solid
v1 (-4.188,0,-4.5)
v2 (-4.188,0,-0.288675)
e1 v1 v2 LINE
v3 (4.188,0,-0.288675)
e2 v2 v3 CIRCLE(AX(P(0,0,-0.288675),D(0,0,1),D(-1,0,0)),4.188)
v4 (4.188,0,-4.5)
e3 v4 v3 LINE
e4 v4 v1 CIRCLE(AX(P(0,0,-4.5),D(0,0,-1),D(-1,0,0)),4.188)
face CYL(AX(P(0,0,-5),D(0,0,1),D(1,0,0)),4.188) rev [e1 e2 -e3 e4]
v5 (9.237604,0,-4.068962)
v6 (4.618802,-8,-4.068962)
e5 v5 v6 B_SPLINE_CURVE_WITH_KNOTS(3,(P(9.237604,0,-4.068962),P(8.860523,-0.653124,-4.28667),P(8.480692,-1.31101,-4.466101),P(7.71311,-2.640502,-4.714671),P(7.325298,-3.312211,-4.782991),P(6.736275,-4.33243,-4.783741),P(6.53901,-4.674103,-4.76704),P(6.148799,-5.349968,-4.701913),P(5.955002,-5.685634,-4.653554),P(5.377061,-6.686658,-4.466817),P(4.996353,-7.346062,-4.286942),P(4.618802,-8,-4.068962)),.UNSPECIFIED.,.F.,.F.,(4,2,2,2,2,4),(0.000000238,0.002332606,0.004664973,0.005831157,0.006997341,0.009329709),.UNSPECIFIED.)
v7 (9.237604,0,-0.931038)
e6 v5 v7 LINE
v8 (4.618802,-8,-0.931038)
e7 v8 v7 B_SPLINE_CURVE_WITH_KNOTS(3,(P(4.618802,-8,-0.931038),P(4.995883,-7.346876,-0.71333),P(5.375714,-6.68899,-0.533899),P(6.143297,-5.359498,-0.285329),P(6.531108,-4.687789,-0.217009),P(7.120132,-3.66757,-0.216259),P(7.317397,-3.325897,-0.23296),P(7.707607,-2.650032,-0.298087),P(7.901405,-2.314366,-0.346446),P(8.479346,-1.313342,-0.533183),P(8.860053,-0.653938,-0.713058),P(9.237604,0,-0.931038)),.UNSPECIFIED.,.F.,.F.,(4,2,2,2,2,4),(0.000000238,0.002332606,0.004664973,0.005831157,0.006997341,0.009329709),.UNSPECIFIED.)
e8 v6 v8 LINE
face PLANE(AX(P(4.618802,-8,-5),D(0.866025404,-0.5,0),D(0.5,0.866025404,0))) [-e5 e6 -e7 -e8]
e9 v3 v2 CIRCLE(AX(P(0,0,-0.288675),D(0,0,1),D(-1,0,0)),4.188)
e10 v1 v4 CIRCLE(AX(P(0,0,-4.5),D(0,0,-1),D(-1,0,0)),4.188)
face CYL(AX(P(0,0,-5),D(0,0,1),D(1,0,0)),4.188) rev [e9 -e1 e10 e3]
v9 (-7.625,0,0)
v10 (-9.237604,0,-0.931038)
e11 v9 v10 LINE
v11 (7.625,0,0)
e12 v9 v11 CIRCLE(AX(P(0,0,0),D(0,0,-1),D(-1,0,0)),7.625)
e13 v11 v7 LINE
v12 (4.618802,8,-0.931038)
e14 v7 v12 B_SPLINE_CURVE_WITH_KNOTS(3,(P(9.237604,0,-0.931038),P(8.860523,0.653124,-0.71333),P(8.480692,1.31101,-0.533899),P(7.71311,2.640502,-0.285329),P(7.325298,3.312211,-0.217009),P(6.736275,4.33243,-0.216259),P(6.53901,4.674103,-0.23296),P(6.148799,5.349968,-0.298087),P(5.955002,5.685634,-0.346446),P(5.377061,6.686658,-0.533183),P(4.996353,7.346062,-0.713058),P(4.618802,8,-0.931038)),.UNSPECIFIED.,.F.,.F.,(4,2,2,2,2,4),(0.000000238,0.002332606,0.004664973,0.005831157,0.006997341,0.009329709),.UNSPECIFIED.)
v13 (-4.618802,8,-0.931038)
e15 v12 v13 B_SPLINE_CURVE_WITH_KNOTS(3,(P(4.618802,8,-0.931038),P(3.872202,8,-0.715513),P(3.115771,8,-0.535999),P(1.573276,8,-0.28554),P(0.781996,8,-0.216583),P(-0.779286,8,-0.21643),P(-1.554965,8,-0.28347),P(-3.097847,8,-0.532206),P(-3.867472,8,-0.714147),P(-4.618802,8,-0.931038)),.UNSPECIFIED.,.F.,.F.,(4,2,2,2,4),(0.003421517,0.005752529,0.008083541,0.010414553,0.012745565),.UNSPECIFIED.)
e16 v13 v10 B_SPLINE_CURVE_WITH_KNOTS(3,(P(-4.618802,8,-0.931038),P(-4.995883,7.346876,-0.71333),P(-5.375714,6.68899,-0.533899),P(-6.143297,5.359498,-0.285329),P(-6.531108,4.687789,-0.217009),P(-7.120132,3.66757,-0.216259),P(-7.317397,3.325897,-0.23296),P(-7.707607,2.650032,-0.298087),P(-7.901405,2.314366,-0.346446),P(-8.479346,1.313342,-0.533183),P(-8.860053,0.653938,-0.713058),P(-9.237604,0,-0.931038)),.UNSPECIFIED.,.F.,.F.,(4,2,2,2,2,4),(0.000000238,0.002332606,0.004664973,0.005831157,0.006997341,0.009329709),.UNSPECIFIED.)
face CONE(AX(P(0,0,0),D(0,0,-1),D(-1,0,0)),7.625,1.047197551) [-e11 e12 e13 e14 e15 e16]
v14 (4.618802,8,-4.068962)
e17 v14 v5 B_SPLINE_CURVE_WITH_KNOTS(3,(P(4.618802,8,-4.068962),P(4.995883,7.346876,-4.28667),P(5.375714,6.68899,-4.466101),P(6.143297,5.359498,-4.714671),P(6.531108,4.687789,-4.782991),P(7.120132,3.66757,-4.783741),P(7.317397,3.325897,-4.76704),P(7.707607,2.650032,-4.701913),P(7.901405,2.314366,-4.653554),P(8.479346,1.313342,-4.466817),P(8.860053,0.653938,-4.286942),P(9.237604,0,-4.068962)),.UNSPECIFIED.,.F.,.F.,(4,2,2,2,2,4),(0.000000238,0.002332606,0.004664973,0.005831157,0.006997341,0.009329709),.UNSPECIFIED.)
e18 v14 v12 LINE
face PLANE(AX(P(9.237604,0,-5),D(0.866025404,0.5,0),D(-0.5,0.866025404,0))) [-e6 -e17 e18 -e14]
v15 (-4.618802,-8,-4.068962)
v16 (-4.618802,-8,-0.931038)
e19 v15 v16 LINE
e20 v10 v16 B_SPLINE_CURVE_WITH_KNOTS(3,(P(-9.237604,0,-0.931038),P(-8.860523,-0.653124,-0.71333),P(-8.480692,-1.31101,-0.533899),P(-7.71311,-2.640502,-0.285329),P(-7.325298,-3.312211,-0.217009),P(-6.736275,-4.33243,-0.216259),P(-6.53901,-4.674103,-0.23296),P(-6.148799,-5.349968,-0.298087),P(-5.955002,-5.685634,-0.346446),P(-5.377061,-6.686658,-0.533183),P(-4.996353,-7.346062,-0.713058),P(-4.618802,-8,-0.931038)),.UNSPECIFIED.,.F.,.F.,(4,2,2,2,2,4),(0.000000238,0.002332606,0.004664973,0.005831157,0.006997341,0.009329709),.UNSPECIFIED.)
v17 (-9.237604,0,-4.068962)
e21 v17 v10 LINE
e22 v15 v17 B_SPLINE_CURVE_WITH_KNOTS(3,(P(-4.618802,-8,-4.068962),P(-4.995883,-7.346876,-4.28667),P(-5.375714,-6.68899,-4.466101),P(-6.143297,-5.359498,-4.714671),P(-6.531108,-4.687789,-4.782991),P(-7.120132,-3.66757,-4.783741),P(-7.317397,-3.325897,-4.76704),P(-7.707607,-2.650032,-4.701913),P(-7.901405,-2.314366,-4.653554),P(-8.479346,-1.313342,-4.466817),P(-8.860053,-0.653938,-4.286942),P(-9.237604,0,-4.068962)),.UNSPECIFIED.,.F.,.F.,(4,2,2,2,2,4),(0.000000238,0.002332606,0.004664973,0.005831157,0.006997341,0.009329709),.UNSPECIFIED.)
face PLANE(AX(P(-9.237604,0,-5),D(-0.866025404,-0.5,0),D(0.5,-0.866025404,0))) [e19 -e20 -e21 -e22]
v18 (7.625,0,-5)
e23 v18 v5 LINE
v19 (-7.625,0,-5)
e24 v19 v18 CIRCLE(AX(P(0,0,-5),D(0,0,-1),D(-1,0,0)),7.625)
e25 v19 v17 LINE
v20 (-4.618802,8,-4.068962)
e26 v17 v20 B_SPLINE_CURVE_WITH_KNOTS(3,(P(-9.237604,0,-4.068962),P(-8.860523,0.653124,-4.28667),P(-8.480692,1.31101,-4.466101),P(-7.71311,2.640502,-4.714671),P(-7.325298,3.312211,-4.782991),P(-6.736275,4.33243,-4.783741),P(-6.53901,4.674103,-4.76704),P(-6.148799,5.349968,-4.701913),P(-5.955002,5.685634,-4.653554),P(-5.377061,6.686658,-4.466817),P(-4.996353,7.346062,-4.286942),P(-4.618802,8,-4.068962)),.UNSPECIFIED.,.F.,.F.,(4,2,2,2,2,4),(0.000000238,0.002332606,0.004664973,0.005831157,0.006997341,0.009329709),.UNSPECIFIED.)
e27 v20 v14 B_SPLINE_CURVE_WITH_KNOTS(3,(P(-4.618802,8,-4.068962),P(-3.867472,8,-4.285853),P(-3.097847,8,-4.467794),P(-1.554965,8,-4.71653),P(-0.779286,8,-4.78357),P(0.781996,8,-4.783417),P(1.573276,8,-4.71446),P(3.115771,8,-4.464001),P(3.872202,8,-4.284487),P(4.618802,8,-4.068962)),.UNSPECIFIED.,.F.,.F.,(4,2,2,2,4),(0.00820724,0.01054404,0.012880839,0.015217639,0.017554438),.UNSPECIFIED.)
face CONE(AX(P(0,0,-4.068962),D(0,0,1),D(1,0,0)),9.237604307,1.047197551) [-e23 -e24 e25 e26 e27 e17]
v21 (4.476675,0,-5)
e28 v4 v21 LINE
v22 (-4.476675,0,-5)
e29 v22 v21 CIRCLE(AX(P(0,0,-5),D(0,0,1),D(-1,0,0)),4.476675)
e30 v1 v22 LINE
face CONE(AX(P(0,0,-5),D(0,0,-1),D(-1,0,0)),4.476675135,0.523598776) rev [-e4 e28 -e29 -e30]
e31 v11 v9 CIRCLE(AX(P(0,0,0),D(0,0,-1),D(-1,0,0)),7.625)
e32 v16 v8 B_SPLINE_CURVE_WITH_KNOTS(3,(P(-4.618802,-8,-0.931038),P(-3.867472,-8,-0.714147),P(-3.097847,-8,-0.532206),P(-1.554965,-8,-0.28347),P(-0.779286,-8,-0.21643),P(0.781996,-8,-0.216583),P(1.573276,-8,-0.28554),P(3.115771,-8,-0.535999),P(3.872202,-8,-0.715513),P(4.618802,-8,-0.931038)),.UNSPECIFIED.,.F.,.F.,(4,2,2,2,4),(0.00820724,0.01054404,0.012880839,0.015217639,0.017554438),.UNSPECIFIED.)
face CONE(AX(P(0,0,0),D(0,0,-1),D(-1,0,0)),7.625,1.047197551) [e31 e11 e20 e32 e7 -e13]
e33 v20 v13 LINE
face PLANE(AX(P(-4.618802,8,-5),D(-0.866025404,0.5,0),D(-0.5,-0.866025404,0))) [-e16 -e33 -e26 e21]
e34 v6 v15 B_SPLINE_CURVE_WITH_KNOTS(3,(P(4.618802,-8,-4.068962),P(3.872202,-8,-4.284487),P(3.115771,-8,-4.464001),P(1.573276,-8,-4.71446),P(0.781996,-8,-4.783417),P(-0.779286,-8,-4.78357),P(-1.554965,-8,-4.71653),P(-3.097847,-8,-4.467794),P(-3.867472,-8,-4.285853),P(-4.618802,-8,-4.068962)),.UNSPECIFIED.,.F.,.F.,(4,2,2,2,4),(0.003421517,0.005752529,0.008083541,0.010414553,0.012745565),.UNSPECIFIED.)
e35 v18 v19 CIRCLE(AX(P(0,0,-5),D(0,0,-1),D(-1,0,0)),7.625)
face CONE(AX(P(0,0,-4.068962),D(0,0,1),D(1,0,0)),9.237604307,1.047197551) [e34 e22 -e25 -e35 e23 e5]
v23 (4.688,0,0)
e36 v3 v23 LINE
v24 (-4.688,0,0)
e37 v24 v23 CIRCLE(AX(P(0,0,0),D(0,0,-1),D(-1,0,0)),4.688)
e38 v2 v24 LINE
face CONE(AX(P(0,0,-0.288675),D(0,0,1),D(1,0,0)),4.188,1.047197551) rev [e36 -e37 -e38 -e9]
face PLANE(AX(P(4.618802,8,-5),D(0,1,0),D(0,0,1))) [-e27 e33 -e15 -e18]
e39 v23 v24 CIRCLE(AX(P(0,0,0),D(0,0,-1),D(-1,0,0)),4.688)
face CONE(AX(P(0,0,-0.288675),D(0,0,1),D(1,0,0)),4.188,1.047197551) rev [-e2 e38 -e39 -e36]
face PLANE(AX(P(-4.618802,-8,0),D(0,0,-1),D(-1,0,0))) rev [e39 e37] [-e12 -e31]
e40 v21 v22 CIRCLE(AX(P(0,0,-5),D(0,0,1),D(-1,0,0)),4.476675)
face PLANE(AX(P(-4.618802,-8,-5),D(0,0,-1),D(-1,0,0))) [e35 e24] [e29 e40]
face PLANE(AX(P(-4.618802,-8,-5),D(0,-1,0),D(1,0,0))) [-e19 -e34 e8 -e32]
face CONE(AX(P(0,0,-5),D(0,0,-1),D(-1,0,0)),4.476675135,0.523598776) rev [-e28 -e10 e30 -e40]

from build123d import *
from OCP.BRepFilletAPI import BRepFilletAPI_MakeChamfer

# Parameters (mm, degrees)
SKETCH1_R        = 4.188
BASENUT_DEPTH    = 5
ENDCHAMFER_SIZE  = 0.5
ENDCHAMFER_SIZE2 = 0.288675135


with BuildPart() as part:
    # Sketch1 → BaseNut (new body)
    with BuildSketch(Plane.XY):
        Polygon((4.618802154, -8), (9.237604307, 0), (4.618802154, 8), (-4.618802154, 8), (-9.237604307, 0), (-4.618802154, -8), align=None)
        Circle(SKETCH1_R, mode=Mode.SUBTRACT)
    extrude(amount=-BASENUT_DEPTH)

    # Sketch2 → Double-Chamfer (revolve, cut)
    with BuildSketch(Plane(origin=(0, 0, 0), x_dir=(1, 0, 0), z_dir=(0, 1, 0))):
        Polygon((-9.237604307, 5), (-7.625, 5), (-9.237604307, 4.068962469), align=None)
        Polygon((-9.237604307, 0.931037531), (-9.237604307, 0), (-7.625, 0), align=None)
    revolve(axis=Axis((0, 0, -3.375940562), (0, 0, 1)), mode=Mode.SUBTRACT)

    # EndChamfer: one chamfer whose edges measure the first distance from different faces: ONE call of the kernel's chamfer builder (chamfer() names one face for all edges)
    endchamfer_edges_1 = [part.edges().sort_by_distance(p)[0] for p in [
        (-4.188, 0, -5),
    ]]
    endchamfer_side_1 = [part.faces().sort_by_distance(p)[0] for p in [
        (-4.188, 0, -2.5),
    ]]
    endchamfer_edges_2 = [part.edges().sort_by_distance(p)[0] for p in [
        (-4.188, 0, 0),
    ]]
    endchamfer_side_2 = [part.faces().sort_by_distance(p)[0] for p in [
        (7.409332432, 0, 0),
    ]]
    endchamfer = BRepFilletAPI_MakeChamfer(part.part.solid().wrapped)
    for e in endchamfer_edges_1:
        endchamfer.Add(ENDCHAMFER_SIZE, ENDCHAMFER_SIZE2, e.wrapped, endchamfer_side_1[0].wrapped)  # the first distance lies on this face
    for e in endchamfer_edges_2:
        endchamfer.Add(ENDCHAMFER_SIZE, ENDCHAMFER_SIZE2, e.wrapped, endchamfer_side_2[0].wrapped)  # the first distance lies on this face
    add(Compound.cast(endchamfer.Shape()), mode=Mode.REPLACE)


solid = part.part
